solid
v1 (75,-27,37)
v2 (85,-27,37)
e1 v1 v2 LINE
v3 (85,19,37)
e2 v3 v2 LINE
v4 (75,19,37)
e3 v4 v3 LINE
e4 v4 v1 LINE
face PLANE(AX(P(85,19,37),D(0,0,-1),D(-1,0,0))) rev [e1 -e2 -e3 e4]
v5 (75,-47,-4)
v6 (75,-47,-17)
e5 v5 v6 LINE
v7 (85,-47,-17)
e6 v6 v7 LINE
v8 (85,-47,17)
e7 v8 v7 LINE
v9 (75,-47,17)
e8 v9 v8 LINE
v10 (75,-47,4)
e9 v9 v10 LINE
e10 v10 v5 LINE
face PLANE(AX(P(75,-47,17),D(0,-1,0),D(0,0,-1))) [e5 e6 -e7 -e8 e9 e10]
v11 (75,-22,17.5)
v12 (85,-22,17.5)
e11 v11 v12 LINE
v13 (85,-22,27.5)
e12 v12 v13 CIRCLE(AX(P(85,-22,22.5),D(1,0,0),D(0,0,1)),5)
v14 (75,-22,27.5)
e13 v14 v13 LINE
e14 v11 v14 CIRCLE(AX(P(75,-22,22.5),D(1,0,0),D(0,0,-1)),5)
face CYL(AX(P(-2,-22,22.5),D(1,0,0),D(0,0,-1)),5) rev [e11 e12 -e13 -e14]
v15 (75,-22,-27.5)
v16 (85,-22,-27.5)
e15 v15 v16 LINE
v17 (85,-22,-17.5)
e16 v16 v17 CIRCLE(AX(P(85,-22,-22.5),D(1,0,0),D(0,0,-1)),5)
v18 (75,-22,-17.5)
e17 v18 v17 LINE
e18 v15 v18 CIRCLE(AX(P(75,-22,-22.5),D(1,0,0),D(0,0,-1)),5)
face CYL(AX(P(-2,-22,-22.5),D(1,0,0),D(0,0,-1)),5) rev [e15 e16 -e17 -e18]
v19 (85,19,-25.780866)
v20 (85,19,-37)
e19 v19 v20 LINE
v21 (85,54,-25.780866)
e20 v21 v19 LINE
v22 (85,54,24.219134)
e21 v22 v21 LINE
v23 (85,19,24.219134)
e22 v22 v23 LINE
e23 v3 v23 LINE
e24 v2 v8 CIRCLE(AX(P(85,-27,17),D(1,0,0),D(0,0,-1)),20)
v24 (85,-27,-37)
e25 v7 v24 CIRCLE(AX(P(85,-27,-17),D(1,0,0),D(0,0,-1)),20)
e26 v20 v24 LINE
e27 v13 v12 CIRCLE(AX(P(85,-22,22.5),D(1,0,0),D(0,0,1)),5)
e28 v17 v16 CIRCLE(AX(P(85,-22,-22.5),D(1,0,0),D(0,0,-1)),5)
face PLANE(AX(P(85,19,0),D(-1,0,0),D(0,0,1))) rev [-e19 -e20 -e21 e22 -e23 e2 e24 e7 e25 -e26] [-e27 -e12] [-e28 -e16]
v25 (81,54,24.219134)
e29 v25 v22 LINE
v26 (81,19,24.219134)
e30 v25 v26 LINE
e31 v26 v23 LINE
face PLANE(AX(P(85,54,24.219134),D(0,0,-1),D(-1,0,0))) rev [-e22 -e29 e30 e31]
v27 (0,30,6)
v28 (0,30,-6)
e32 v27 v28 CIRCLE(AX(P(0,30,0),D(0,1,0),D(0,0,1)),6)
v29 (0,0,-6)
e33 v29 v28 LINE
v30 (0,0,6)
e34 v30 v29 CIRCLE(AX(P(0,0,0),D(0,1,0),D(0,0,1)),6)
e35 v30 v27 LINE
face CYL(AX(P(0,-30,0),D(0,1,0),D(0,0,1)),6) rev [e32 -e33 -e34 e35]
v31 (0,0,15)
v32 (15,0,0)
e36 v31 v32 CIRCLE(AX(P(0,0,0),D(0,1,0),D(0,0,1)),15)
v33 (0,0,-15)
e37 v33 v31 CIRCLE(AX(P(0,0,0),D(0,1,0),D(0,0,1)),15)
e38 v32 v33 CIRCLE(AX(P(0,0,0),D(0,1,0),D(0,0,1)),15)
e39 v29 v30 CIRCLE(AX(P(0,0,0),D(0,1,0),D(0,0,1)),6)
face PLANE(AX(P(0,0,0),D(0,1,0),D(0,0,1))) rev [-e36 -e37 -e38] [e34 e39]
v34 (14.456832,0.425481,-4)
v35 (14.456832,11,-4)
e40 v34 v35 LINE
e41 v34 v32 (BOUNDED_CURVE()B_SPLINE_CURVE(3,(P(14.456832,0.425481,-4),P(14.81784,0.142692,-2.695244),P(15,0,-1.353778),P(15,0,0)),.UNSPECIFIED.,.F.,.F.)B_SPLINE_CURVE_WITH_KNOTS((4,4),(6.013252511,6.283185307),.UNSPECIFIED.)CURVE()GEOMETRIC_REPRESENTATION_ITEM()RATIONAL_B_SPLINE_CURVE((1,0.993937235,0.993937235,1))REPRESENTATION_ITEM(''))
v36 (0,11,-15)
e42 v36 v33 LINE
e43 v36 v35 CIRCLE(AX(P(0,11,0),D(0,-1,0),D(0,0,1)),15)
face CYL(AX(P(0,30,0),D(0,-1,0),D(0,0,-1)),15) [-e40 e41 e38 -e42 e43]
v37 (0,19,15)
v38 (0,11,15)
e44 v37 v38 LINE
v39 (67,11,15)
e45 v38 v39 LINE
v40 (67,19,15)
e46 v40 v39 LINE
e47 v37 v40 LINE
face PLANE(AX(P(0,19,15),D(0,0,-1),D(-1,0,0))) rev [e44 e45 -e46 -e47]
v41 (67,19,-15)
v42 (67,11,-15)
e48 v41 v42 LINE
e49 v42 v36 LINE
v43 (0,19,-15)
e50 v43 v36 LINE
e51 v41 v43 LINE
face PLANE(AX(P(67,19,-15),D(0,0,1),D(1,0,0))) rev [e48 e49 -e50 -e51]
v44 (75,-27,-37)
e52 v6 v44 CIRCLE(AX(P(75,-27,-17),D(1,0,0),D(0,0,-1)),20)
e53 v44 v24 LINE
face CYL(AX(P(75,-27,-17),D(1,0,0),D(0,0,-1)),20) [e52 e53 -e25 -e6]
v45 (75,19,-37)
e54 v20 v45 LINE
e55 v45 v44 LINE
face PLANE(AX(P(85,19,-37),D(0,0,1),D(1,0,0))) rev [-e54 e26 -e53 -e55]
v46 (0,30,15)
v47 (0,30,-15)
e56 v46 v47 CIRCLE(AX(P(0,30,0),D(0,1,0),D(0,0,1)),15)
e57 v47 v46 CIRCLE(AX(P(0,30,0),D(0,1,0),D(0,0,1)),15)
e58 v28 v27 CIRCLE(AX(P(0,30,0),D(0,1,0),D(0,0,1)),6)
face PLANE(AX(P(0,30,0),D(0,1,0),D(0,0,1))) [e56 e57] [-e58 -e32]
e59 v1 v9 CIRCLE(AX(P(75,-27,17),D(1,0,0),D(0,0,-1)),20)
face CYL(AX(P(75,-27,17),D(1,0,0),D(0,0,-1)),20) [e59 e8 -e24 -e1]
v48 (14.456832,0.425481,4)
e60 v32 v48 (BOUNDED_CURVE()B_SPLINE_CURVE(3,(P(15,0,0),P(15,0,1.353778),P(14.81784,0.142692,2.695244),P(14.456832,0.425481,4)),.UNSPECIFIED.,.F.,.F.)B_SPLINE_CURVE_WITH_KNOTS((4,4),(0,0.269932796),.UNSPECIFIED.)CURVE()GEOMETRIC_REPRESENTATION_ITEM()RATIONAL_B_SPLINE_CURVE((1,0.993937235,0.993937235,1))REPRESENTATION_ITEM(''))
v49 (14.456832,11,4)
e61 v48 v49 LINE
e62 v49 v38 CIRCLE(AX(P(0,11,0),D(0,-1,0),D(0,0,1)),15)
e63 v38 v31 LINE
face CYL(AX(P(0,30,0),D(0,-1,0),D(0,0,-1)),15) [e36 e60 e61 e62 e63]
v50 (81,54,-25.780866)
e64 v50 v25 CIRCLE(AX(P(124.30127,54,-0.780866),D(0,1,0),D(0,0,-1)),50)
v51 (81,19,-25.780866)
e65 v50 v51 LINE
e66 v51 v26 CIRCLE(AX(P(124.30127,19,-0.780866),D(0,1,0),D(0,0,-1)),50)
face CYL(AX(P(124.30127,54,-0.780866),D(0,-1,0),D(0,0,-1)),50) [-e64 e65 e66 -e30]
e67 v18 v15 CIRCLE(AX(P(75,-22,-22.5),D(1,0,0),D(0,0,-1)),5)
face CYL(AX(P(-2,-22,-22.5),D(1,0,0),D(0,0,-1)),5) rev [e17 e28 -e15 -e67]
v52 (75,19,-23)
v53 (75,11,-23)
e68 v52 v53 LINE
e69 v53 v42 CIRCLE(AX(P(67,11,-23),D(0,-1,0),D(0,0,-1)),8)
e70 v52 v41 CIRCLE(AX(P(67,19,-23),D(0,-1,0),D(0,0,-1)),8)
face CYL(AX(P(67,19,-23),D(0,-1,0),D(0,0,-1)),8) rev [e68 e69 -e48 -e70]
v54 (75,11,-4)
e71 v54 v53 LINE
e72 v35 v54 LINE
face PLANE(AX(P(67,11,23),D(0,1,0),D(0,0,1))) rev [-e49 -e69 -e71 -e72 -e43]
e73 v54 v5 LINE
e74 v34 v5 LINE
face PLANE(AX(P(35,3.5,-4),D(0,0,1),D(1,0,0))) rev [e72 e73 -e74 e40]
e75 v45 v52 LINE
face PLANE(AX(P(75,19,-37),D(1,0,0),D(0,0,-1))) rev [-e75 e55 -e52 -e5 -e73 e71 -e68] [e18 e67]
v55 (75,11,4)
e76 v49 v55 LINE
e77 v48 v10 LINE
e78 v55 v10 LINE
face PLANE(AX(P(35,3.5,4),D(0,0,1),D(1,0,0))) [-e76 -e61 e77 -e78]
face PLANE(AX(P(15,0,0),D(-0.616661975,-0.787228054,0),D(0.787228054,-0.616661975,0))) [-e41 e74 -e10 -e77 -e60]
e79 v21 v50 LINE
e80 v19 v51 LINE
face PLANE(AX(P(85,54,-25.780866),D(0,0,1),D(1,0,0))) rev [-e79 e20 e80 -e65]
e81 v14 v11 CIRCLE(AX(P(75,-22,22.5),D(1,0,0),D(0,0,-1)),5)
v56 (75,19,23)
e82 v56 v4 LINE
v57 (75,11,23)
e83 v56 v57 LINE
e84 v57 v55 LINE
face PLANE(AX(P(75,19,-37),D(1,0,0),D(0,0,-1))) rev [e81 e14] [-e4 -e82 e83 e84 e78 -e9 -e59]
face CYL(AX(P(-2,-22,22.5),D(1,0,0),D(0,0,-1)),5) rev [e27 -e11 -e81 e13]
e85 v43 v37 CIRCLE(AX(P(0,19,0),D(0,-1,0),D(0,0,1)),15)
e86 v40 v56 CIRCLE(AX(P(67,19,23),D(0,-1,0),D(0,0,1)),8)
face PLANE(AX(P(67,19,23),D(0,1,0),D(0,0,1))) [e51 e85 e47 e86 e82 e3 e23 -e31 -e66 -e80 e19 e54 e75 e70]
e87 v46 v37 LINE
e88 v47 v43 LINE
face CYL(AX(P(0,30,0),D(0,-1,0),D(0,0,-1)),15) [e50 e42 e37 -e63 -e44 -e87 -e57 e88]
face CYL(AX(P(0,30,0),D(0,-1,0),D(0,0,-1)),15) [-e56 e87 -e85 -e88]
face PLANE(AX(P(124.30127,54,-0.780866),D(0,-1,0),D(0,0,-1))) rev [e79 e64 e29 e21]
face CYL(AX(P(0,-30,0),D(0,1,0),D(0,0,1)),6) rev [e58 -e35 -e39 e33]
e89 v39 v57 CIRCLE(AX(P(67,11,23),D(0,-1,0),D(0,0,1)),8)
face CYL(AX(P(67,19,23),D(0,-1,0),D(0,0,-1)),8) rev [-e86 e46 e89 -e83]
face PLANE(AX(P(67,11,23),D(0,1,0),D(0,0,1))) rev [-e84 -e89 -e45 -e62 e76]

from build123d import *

# Parameters (mm, degrees)
HUB_PROFILE_R              = 15
HUB_30_DEPTH               = 30
BORE_PROFILE_R             = 6
BORE_12_DEPTH              = 60
ARM_DEPTH                  = 4
MOUNTING_PLATE_DEPTH       = 35
PLATE_LUG_DEPTH            = 10
MOUNTING_HOLES_PROFILE_R   = 5
MOUNTING_HOLES_2X_10_DEPTH = 87
SUPPORT_RIB_REACH          = 109.285
RIB_LINE_WALL_W            = 292.786132162
RIB_LINE_WALL_H            = 8


with BuildPart() as part:
    # Hub Profile → Hub Ø30 (new body)
    with BuildSketch(Plane(origin=(0, 0, 0), x_dir=(1, 0, 0), z_dir=(0, 1, 0))):
        with Locations(Location((0, 0, 0), (0, 0, 270))):
            Circle(HUB_PROFILE_R)
    extrude(amount=HUB_30_DEPTH)

    # Bore Profile → Bore Ø12 (cut)
    with BuildSketch(Plane(origin=(0, 30, 0), x_dir=(1, 0, 0), z_dir=(0, 1, 0))):
        with Locations(Location((0, 0, 0), (0, 0, 270))):
            Circle(BORE_PROFILE_R)
    extrude(amount=-BORE_12_DEPTH, mode=Mode.SUBTRACT)

    # Arm Profile → Arm (add, symmetric)
    with BuildSketch(Plane(origin=(0, 15, 0), x_dir=(1, 0, 0), z_dir=(0, 1, 0))):
        with BuildLine():
            Line((85, 0), (85, 37))
            Line((85, 37), (75, 37))
            Line((75, 37), (75, 23))
            ThreePointArc((75, 23), (72.656854249, 17.343145751), (67, 15))
            Line((67, 15), (0, 15))
            ThreePointArc((0, 15), (15, 0), (0, -15))
            Line((0, -15), (67, -15))
            ThreePointArc((67, -15), (72.656854249, -17.343145751), (75, -23))
            Line((75, -23), (75, -37))
            Line((75, -37), (85, -37))
            Line((85, -37), (85, 0))
        make_face()
    extrude(amount=ARM_DEPTH, both=True)

    # Mounting Plate Profile → Mounting Plate (add)
    with BuildSketch(Plane(origin=(0, 19, 0), x_dir=(1, 0, 0), z_dir=(0, 1, 0))):
        with BuildLine():
            Line((85, 0.780866297), (85, 25.780866297))
            Line((85, 25.780866297), (81, 25.780866297))
            ThreePointArc((81, 25.780866297), (74.301270189, 0.780866297), (81, -24.219133703))
            Line((81, -24.219133703), (85, -24.219133703))
            Line((85, -24.219133703), (85, 0.780866297))
        make_face()
    extrude(amount=MOUNTING_PLATE_DEPTH)

    # Plate Lug Profile → Plate Lug (add)
    with BuildSketch(Plane(origin=(85, 0, 0), x_dir=(0, 0, -1), z_dir=(1, 0, 0))):
        with BuildLine():
            Line((-37, 11), (-37, -27))
            ThreePointArc((-37, -27), (-31.142135624, -41.142135624), (-17, -47))
            Line((-17, -47), (17, -47))
            ThreePointArc((17, -47), (31.142135624, -41.142135624), (37, -27))
            Line((37, -27), (37, 11))
            Line((37, 11), (-37, 11))
        make_face()
    extrude(amount=-PLATE_LUG_DEPTH)

    # Mounting Holes Profile → Mounting Holes 2xØ10 (cut)
    with BuildSketch(Plane(origin=(85, 0, 0), x_dir=(0, 0, -1), z_dir=(1, 0, 0))):
        with Locations((22.5, -22)):
            Circle(MOUNTING_HOLES_PROFILE_R)
        with Locations((-22.5, -22)):
            Circle(MOUNTING_HOLES_PROFILE_R)
    extrude(amount=-MOUNTING_HOLES_2X_10_DEPTH, mode=Mode.SUBTRACT)

    # Rib Line wall → Support Rib (add, up to next)
    with BuildSketch(Plane(origin=(45, -23.5, 0), x_dir=(0.787228053529, -0.616661975264, 0), z_dir=(0.616661975264, 0.787228053529, 0)), mode=Mode.PRIVATE) as support_rib_sk1:
        Rectangle(RIB_LINE_WALL_W, RIB_LINE_WALL_H)
    support_rib_tool1 = extrude(support_rib_sk1.sketch, amount=SUPPORT_RIB_REACH, mode=Mode.PRIVATE) - part.part
    add(support_rib_tool1.solids().sort_by_distance((45, -23.5, 0))[0])


solid = part.part
